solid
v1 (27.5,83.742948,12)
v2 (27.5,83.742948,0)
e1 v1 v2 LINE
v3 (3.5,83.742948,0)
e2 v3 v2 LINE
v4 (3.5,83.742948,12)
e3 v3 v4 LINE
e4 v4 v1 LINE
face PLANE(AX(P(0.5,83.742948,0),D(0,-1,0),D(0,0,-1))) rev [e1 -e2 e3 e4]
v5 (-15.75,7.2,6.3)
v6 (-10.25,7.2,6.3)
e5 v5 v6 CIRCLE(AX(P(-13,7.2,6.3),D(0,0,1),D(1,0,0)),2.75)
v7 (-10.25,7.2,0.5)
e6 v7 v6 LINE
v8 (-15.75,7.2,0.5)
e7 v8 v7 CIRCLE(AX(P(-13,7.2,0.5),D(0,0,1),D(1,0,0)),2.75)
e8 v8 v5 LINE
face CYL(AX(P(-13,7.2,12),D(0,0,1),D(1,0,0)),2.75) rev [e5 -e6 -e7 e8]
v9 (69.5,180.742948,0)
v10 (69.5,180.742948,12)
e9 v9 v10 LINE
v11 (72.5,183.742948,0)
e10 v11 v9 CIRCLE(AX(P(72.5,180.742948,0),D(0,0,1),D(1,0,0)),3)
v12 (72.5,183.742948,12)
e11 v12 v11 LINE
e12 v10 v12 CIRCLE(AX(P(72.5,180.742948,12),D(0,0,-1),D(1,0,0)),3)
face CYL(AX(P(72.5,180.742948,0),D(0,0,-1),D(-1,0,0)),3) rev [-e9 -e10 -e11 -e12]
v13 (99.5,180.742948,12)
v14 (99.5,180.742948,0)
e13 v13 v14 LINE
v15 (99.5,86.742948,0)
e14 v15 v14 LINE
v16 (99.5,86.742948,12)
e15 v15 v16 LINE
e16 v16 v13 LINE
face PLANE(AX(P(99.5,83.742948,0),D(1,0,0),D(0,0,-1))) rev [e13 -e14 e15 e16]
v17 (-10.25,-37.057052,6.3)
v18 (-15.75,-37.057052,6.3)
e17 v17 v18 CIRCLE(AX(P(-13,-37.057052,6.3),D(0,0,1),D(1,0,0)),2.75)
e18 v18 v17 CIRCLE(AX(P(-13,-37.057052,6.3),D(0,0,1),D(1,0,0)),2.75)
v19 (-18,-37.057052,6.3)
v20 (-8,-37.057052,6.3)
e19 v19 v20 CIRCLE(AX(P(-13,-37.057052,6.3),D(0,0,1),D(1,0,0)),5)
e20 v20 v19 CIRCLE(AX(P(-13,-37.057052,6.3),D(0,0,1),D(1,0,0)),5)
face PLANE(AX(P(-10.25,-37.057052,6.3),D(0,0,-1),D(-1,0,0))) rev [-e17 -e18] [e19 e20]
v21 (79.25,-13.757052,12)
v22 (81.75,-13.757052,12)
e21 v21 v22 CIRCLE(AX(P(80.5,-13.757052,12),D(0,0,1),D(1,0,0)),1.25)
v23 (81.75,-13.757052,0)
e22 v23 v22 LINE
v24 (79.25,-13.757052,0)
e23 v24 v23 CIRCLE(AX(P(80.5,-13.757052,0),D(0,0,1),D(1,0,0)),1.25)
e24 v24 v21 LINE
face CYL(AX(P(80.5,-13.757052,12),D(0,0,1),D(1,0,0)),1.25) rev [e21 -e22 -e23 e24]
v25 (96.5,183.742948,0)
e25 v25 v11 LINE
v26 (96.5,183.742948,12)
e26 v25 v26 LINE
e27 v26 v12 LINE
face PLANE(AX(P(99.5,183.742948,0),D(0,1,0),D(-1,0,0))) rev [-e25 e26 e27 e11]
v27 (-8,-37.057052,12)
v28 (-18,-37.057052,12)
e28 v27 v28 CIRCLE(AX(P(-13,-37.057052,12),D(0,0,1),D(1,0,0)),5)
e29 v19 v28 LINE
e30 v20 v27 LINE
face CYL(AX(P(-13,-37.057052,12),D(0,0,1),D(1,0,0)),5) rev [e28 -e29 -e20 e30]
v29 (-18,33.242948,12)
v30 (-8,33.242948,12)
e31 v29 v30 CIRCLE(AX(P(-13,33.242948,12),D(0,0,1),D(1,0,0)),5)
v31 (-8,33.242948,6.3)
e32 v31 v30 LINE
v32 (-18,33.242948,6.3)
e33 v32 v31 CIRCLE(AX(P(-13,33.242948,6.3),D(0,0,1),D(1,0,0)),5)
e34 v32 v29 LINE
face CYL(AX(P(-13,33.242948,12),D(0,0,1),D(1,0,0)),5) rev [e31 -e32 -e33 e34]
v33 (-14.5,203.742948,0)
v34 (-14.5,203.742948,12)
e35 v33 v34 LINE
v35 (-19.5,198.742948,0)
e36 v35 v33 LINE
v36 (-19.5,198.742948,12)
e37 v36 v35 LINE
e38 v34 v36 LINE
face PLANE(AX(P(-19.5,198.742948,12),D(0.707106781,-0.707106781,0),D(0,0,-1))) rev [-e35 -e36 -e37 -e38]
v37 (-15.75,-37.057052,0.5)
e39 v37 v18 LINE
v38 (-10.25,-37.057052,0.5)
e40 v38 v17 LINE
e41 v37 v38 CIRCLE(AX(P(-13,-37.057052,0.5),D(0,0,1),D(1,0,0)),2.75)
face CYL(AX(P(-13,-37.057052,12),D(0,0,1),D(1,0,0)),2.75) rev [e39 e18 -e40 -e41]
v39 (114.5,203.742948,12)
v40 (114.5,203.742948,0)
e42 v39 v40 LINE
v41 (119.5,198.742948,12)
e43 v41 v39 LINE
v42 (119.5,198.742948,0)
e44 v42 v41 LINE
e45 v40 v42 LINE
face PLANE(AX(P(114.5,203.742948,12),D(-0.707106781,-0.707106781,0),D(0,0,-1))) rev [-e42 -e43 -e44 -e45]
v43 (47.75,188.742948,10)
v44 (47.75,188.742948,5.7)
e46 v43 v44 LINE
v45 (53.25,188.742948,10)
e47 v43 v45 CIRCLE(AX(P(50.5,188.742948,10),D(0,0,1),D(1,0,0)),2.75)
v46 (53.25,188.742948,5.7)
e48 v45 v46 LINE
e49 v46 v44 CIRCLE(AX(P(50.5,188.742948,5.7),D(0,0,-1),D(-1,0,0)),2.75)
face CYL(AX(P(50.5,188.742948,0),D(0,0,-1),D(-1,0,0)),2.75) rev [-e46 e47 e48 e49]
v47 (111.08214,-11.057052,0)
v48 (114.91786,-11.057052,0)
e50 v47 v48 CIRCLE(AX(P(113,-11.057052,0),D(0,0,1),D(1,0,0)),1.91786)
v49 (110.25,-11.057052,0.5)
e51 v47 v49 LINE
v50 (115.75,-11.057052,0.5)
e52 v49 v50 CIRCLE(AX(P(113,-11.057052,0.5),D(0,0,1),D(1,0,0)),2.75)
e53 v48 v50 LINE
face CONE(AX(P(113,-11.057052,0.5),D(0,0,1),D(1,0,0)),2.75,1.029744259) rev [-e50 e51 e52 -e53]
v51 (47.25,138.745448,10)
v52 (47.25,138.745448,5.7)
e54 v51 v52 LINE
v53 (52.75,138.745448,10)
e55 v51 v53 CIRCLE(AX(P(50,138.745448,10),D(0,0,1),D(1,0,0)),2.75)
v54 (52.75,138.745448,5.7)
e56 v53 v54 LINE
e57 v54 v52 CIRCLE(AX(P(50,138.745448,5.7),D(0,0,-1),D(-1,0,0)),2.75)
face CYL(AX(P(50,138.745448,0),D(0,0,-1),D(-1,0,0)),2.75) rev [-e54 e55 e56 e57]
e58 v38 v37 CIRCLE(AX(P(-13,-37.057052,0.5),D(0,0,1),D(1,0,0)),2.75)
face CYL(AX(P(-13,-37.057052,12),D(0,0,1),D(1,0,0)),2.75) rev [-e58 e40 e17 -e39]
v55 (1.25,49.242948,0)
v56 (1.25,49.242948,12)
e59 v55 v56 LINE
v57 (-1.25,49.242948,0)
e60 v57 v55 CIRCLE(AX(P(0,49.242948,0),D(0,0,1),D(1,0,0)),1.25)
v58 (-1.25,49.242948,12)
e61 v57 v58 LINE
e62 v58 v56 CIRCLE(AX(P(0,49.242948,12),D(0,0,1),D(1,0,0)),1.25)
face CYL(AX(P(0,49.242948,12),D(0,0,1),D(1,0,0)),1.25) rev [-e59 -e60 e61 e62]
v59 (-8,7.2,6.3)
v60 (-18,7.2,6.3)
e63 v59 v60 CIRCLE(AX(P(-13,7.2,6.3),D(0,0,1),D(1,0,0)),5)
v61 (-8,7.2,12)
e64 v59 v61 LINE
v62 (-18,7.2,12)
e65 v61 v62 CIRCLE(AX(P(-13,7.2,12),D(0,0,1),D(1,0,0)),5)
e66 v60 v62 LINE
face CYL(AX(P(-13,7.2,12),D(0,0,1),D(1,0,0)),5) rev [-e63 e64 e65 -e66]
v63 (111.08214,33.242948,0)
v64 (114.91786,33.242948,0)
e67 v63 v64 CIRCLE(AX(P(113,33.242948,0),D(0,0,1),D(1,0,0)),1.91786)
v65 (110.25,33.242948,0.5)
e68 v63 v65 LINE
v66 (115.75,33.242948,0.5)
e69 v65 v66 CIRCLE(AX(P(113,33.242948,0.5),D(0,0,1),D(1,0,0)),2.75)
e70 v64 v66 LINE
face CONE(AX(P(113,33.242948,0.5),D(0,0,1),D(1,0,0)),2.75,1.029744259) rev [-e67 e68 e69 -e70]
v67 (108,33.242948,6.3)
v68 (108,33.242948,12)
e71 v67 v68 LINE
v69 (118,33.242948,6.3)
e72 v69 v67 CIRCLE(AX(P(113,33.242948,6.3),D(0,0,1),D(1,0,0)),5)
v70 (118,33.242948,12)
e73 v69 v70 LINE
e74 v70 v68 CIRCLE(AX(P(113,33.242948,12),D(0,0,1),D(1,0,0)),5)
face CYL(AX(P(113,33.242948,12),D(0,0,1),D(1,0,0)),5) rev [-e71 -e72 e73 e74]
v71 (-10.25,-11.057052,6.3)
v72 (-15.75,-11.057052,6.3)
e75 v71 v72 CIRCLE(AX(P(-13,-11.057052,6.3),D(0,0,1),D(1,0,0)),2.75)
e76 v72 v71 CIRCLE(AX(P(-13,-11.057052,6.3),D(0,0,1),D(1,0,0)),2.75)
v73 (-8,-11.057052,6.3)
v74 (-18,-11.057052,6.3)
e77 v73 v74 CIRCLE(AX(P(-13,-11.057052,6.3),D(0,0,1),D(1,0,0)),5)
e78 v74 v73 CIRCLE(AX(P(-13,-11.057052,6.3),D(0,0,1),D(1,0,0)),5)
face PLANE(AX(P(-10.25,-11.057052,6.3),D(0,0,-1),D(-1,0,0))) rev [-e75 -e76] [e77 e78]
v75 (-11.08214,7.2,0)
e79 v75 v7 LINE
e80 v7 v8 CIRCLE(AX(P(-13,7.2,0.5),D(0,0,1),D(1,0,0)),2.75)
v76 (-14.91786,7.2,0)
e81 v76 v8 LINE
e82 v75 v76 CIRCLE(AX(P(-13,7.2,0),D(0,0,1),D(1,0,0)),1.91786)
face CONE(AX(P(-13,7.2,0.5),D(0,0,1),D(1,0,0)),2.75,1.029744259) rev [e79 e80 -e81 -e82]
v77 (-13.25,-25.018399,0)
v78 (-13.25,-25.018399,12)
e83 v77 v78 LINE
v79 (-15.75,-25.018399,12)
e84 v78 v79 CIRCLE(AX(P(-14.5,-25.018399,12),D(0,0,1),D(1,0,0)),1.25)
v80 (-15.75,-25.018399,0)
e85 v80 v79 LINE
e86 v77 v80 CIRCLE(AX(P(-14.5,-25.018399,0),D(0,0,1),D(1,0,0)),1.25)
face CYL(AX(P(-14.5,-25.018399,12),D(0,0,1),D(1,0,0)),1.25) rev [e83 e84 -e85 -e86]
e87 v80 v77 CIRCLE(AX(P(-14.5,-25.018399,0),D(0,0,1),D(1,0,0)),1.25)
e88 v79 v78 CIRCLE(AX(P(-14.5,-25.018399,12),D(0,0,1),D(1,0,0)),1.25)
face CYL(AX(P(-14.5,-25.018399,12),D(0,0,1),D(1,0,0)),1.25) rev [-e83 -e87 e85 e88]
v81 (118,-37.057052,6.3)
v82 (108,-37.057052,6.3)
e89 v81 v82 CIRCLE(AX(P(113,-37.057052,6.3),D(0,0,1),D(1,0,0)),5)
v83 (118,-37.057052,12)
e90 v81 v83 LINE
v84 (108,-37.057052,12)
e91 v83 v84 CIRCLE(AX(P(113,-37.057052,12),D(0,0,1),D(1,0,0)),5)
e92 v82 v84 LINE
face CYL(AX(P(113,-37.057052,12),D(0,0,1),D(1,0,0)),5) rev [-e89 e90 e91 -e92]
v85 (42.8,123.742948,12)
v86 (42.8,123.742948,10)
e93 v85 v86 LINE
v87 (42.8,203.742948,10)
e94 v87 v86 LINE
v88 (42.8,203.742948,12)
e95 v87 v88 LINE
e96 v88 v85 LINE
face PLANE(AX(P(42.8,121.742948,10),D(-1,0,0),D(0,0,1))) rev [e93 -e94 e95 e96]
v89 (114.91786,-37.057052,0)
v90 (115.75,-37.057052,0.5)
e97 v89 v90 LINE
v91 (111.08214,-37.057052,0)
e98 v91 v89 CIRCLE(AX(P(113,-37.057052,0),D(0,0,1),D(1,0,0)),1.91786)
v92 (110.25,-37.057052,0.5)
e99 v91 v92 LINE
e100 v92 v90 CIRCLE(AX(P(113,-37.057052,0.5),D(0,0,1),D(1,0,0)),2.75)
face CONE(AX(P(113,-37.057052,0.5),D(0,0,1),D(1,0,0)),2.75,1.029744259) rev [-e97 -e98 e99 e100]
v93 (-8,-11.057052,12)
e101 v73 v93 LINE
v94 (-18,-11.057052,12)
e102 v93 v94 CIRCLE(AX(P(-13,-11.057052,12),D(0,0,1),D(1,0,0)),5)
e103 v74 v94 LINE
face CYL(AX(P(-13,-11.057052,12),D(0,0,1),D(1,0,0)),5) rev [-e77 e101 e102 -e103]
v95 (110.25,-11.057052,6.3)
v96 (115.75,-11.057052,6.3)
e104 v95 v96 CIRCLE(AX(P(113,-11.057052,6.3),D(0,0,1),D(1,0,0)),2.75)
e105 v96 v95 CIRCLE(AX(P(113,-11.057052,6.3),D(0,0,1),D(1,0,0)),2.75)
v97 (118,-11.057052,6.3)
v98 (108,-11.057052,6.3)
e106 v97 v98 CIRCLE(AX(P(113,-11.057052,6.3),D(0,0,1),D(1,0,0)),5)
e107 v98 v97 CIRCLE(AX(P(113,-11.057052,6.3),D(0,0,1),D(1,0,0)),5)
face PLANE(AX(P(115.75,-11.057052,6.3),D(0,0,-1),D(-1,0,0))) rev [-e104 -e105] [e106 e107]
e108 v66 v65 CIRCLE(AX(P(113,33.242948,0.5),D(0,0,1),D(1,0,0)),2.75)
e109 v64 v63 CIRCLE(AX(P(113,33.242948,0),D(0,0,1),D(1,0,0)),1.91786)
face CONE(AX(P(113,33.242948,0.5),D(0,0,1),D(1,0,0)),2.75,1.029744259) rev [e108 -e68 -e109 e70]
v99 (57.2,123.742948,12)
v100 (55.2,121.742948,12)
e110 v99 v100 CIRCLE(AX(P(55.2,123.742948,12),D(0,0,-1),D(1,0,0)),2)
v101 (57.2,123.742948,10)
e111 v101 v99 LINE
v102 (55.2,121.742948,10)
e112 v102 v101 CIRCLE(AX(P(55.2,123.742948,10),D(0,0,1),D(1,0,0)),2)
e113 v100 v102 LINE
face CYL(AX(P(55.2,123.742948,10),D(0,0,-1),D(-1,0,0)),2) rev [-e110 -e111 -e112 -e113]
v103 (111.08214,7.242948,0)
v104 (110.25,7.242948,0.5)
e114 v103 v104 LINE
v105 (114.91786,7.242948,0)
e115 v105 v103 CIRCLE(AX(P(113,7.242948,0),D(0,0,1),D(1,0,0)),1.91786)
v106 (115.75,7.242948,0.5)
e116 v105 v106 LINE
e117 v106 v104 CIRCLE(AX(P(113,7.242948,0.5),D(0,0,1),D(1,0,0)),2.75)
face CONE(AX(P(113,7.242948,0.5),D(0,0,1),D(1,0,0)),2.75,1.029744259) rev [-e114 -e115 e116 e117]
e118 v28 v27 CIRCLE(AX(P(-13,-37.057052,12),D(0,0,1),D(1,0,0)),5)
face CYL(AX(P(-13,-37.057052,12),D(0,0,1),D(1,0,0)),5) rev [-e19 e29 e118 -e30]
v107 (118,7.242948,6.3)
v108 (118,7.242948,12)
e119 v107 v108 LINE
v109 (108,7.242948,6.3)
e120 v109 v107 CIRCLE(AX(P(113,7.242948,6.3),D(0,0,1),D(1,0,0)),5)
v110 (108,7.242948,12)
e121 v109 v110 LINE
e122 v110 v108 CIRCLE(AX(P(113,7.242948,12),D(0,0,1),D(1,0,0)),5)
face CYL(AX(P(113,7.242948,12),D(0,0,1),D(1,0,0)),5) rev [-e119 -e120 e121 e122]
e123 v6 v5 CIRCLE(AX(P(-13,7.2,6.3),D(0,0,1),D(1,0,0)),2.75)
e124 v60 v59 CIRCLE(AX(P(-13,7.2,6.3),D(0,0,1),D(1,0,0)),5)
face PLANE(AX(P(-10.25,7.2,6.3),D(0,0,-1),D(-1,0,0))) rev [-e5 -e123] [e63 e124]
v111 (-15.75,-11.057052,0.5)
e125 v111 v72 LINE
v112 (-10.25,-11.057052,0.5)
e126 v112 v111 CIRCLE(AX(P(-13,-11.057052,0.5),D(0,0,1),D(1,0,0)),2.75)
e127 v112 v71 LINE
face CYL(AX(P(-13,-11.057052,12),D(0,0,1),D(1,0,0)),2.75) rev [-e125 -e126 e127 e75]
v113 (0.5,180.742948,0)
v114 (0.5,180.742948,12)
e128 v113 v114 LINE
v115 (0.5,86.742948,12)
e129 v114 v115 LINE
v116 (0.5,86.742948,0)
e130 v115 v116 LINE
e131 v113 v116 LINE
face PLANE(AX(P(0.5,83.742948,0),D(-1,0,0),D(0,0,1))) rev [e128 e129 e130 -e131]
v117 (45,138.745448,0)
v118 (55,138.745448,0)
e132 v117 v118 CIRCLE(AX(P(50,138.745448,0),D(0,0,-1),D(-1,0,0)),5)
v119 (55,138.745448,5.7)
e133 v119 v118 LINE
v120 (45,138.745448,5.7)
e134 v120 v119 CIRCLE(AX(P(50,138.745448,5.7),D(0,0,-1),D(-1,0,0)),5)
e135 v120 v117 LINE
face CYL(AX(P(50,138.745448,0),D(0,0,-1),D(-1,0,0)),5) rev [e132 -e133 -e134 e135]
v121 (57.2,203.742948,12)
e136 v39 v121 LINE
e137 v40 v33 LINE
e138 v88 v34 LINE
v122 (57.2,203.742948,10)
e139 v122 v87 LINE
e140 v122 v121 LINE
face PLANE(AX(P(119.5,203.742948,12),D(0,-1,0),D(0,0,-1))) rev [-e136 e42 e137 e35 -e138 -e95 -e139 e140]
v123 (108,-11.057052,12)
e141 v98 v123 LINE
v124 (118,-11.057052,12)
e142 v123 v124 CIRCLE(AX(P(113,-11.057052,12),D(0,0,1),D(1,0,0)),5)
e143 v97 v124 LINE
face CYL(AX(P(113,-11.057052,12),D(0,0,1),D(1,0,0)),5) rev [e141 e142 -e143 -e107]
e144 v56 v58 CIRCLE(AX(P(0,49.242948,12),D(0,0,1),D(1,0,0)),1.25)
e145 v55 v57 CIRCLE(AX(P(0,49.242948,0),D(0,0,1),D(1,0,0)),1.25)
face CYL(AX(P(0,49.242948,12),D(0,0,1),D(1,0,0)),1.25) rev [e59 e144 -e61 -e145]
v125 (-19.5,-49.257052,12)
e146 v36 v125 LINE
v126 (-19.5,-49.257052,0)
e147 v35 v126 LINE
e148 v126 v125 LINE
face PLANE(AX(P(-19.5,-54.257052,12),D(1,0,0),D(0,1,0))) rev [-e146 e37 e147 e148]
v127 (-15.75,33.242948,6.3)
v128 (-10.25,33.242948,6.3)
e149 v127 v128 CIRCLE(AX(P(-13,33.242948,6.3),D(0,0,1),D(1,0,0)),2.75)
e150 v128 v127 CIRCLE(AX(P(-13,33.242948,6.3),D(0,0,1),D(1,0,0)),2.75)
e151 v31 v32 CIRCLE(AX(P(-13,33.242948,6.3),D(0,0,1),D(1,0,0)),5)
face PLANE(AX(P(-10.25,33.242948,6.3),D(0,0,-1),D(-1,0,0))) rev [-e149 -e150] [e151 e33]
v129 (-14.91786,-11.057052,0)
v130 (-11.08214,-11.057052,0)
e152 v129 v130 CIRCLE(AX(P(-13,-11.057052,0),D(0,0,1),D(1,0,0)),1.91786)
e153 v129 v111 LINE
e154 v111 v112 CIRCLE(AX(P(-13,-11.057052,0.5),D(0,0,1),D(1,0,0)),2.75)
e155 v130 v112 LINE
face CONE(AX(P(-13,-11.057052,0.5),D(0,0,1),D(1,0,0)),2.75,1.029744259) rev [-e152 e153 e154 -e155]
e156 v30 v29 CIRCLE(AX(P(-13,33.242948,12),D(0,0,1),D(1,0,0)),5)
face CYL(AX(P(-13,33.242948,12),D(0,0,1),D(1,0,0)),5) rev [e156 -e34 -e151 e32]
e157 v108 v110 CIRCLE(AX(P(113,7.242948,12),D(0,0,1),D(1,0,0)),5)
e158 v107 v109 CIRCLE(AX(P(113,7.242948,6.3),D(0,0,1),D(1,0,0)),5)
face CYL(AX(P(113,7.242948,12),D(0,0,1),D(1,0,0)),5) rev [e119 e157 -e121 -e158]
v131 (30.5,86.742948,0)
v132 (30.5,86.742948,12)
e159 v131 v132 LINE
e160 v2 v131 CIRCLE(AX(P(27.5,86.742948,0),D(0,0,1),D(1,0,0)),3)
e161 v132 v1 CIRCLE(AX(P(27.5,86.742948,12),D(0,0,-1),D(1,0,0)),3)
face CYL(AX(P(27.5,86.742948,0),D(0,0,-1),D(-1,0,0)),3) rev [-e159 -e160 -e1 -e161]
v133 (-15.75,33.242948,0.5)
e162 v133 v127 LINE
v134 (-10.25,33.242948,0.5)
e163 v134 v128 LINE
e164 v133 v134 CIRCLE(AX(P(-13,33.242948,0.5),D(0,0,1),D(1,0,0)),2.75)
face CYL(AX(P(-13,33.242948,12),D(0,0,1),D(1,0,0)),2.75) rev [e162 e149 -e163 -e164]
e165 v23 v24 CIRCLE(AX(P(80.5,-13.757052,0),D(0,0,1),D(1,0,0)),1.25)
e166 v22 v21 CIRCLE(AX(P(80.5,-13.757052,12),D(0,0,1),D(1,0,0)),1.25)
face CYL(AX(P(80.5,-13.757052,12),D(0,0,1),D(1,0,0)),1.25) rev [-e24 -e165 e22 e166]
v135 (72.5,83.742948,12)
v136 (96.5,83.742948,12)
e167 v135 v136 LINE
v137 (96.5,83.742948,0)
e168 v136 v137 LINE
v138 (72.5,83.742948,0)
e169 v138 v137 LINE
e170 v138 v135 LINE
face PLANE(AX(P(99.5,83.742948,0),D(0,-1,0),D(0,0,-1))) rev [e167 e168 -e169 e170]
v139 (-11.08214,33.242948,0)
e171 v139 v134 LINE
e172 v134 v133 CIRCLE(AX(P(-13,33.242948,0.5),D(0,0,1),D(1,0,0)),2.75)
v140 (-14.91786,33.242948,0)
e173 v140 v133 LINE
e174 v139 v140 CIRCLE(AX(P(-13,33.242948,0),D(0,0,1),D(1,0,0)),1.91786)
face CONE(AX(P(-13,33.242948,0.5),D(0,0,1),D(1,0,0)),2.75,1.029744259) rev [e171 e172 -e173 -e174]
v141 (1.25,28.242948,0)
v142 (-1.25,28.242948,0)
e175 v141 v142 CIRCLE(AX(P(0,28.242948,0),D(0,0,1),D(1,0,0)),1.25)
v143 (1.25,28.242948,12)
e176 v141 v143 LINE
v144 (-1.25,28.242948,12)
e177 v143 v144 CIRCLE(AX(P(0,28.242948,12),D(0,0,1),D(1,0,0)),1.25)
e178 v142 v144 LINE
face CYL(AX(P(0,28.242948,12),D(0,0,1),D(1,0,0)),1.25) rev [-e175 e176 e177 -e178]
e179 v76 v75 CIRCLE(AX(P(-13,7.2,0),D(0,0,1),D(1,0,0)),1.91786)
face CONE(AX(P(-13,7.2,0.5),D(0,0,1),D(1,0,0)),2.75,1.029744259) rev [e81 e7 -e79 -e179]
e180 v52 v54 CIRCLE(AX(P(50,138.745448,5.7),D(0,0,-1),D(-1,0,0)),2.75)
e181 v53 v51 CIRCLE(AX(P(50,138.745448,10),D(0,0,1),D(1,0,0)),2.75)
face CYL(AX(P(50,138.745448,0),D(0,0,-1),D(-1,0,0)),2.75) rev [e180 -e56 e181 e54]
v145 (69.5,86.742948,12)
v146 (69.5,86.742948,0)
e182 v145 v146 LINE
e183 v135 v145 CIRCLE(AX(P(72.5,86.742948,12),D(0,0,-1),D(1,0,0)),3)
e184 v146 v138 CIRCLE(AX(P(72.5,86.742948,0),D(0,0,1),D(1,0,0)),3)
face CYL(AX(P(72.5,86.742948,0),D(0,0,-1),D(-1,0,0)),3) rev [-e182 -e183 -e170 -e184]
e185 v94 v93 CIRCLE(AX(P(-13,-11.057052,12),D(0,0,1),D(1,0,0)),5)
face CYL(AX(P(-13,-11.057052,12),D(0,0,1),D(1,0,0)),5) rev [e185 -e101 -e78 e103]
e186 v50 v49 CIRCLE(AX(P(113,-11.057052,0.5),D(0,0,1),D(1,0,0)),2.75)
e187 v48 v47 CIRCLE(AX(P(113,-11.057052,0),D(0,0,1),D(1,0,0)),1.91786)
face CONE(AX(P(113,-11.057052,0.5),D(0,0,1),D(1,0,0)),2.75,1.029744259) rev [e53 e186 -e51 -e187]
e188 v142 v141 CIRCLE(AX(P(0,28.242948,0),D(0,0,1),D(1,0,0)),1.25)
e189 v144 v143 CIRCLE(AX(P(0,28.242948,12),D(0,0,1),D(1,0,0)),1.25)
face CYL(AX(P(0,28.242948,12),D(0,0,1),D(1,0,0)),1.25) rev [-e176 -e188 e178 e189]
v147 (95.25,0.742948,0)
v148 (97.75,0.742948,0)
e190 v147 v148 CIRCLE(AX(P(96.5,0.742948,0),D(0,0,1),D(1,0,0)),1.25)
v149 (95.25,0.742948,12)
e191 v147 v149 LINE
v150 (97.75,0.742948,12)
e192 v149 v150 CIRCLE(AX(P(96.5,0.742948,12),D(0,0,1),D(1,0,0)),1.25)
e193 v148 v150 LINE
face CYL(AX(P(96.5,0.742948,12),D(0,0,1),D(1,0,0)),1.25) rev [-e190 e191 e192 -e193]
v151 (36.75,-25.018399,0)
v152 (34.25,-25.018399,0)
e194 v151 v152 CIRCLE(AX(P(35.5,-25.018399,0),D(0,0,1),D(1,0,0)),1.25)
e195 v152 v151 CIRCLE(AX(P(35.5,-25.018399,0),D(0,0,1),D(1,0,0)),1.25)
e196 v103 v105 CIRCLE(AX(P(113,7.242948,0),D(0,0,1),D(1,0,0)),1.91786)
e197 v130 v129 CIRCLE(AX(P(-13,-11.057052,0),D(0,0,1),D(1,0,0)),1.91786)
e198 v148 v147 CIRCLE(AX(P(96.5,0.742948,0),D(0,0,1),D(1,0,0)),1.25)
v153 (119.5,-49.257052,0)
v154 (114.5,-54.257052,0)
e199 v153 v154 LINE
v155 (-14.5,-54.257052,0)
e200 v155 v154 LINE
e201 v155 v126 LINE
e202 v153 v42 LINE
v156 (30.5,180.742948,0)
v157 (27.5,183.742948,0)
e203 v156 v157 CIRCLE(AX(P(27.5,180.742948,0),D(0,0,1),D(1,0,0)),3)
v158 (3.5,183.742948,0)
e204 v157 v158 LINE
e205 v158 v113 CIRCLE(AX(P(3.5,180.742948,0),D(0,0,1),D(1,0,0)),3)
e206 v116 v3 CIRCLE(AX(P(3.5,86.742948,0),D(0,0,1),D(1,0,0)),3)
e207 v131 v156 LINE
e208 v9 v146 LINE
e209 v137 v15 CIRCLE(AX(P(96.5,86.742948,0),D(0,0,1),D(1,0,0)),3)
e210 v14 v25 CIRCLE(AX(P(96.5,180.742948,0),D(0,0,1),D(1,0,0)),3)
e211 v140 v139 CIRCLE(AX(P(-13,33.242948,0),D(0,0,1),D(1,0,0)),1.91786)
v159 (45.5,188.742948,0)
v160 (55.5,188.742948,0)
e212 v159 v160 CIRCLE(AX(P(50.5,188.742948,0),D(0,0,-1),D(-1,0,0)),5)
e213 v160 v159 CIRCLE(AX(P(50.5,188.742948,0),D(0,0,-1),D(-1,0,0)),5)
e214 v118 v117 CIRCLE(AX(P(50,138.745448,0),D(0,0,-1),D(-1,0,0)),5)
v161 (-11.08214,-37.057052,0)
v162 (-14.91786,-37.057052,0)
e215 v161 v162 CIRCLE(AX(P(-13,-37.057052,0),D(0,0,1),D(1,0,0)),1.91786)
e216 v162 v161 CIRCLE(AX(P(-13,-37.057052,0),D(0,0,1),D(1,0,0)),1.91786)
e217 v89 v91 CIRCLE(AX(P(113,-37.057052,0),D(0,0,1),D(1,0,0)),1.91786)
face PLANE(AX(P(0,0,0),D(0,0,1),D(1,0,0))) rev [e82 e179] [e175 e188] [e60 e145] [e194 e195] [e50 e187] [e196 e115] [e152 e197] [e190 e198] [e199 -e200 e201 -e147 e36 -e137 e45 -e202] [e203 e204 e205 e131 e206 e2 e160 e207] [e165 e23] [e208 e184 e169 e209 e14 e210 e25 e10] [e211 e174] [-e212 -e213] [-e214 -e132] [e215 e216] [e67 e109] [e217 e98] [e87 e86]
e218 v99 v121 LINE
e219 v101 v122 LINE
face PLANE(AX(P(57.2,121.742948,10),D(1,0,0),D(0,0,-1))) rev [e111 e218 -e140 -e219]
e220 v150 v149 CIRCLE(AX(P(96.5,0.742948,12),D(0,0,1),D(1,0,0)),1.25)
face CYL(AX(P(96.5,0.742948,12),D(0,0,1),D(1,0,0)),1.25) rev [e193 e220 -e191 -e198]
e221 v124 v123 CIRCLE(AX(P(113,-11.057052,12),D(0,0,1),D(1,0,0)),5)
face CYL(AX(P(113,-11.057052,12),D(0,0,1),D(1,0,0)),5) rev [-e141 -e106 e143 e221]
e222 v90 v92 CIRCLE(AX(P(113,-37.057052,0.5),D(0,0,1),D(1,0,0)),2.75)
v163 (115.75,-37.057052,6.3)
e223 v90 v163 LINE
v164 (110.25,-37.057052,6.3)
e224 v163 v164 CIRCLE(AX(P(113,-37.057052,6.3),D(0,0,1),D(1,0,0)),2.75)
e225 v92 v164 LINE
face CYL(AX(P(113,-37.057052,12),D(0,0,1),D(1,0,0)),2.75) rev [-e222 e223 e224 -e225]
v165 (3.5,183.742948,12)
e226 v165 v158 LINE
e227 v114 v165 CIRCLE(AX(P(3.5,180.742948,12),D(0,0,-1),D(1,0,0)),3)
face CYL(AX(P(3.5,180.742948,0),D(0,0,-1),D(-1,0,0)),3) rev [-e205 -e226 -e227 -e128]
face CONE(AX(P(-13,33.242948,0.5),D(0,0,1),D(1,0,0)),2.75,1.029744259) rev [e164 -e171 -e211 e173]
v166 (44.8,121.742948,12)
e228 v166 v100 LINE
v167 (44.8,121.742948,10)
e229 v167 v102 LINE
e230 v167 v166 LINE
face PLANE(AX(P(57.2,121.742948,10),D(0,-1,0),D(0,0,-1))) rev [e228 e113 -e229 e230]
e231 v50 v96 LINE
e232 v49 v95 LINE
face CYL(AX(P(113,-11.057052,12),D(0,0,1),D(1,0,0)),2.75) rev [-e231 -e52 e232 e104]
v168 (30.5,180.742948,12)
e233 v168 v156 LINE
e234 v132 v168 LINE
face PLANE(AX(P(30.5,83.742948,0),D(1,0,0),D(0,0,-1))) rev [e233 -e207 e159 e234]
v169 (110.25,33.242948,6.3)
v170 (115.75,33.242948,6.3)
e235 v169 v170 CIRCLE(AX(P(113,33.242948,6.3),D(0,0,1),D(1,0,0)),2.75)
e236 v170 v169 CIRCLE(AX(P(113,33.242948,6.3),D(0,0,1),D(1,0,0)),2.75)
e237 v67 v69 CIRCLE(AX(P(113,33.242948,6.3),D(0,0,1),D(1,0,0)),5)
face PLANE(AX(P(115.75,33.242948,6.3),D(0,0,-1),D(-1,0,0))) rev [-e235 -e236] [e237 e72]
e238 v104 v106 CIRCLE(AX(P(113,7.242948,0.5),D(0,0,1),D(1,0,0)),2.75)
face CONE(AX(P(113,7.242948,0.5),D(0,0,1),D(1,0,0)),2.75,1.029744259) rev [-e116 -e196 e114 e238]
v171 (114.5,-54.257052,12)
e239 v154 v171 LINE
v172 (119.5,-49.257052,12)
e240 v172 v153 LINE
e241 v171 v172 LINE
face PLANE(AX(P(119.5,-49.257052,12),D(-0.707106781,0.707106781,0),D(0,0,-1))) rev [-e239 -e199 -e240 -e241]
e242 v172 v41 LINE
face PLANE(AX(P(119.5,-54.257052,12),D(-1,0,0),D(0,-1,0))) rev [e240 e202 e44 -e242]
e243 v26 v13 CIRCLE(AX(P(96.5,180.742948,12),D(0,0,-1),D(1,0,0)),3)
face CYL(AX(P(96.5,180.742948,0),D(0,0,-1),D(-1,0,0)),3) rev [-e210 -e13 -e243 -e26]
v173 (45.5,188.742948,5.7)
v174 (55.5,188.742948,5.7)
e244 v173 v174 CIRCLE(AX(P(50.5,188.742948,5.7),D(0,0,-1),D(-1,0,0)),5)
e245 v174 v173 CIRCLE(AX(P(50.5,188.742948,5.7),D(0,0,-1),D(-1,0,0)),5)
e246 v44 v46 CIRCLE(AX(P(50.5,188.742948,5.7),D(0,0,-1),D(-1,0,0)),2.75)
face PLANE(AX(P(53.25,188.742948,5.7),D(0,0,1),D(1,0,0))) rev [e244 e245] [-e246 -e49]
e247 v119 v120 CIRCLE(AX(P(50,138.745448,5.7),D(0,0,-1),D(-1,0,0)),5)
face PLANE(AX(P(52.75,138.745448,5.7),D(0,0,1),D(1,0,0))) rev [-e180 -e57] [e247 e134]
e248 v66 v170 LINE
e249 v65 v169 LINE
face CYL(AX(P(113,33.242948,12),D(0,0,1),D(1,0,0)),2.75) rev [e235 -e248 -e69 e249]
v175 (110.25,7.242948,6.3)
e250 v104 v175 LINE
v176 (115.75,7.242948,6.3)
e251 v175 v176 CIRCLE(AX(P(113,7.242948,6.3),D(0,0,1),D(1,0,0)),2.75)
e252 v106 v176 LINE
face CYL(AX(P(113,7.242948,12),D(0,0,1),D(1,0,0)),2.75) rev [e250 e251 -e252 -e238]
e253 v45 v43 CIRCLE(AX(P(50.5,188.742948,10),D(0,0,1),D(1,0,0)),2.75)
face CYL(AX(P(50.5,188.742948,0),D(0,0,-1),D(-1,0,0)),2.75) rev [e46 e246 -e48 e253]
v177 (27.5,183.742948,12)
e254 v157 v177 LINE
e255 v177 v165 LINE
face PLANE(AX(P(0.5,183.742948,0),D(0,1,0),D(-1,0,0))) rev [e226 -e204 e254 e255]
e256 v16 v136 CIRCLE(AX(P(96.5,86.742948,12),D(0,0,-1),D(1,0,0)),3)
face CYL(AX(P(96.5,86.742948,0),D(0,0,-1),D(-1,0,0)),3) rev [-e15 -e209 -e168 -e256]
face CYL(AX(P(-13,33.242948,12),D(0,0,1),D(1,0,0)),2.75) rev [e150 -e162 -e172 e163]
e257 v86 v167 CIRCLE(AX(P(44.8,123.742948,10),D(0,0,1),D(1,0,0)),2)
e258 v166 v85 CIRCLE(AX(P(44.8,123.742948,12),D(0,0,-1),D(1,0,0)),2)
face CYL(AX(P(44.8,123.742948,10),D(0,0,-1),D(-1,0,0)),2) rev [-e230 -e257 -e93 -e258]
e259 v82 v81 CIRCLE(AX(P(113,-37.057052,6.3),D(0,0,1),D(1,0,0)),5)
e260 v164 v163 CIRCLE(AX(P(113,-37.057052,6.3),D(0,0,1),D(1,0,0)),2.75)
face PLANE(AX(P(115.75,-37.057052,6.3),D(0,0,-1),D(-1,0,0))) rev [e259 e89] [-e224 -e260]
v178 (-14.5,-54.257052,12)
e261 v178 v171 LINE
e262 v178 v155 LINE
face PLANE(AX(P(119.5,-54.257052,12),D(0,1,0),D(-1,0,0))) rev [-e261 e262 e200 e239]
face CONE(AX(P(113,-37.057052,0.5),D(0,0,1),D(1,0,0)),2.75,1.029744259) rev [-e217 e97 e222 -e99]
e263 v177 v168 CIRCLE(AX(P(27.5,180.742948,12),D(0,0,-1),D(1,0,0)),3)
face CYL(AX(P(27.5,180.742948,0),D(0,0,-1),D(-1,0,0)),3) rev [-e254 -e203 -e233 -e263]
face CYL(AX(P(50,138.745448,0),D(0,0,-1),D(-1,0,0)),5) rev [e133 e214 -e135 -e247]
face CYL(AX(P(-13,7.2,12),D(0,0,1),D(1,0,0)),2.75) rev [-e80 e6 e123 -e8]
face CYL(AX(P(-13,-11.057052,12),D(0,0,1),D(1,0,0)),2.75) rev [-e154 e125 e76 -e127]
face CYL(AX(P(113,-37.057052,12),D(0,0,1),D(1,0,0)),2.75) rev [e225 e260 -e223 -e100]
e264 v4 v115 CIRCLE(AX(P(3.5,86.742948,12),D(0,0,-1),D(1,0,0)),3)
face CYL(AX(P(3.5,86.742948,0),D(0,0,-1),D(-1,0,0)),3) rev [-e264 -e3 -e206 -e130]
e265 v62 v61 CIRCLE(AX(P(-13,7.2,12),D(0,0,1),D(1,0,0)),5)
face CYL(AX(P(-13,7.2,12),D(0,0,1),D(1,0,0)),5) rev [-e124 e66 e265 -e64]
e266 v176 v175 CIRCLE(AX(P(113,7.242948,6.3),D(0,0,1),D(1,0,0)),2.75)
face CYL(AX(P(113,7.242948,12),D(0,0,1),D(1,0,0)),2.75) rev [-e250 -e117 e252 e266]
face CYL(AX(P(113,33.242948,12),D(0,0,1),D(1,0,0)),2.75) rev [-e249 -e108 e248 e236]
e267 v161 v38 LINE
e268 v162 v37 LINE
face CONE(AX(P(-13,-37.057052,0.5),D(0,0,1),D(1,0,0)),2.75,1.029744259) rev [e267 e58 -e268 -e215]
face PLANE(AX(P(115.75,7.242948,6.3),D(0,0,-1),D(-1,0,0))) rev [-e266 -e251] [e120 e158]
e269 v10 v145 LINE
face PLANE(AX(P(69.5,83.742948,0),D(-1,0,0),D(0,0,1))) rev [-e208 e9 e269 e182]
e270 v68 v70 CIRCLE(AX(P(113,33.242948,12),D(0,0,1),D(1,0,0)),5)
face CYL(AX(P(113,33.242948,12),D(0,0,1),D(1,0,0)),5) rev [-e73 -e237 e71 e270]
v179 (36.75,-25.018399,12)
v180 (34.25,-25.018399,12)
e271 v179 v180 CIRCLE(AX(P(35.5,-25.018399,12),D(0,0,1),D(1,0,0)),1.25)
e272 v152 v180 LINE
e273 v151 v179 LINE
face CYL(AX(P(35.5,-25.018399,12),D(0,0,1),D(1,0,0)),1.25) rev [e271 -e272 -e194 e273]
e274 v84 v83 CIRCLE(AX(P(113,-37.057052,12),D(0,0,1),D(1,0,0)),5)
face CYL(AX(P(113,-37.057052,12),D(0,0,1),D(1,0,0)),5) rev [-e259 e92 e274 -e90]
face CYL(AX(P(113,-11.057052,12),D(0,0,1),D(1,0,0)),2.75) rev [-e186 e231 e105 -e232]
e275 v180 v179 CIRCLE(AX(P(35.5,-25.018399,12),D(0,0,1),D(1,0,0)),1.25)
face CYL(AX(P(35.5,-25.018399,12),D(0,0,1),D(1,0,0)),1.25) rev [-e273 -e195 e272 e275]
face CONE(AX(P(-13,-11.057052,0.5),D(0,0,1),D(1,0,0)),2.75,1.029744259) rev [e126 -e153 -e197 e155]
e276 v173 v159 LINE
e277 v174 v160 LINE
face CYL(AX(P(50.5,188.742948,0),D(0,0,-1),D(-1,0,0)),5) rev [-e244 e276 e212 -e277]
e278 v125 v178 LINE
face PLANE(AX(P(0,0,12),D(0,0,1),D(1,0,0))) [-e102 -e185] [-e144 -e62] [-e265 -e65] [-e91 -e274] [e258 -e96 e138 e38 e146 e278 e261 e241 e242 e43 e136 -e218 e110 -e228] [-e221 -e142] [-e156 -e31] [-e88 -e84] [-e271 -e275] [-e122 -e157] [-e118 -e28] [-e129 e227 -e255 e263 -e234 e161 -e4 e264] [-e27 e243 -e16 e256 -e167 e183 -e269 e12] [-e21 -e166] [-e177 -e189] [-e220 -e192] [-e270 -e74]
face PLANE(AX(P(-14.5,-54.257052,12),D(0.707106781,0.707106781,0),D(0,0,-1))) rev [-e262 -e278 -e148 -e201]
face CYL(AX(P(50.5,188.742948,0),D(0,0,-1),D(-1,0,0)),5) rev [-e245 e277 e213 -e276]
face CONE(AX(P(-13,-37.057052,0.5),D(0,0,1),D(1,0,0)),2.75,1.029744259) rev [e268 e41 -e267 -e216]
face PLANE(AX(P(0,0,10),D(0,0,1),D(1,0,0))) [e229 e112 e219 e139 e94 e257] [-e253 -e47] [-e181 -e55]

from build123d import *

# Parameters (mm, degrees)
SKETCH1_W                                            = 139
SKETCH1_H                                            = 258
BOSS_EXTRUDE1_DEPTH                                  = 12
CHAMFER1_SIZE                                        = 5
SKETCH2_W                                            = 30
SKETCH2_H                                            = 100
CUT_EXTRUDE1_DEPTH                                   = 237.506741929
SKETCH3_W                                            = 14.4
SKETCH3_H                                            = 82
CUT_EXTRUDE2_DEPTH                                   = 2
FILLET1_R                                            = 2
M3_TAPPED_HOLE1_D                                    = 2.5
M3_TAPPED_HOLE2_D                                    = 2.5
CBORE_FOR_M5_HEXAGON_SOCKET_HEAD_CAP_SCR_D           = 5.5
CBORE_FOR_M5_HEXAGON_SOCKET_HEAD_CAP_SCR_CBORE_D     = 10
CBORE_FOR_M5_HEXAGON_SOCKET_HEAD_CAP_SCR_CBORE_DEPTH = 5.7
FILLET2_R                                            = 3
CBORE_FOR_M5_HEXAGON_SOCKET_HEAD_CAP_2_D             = 5.5
CBORE_FOR_M5_HEXAGON_SOCKET_HEAD_CAP_2_DEPTH         = 11.5
CBORE_FOR_M5_HEXAGON_SOCKET_HEAD_CAP_2_CBORE_D       = 10
CBORE_FOR_M5_HEXAGON_SOCKET_HEAD_CAP_2_CBORE_DEPTH   = 5.7
CBORE_FOR_M5_HEXAGON_SOCKET_HEAD_CAP_2_TIP           = 1.652366702


with BuildPart() as part:
    # Sketch1 → Boss-Extrude1 (new body)
    with BuildSketch(Plane.XY):
        with Locations((50, 74.74294829)):
            Rectangle(SKETCH1_W, SKETCH1_H)
    extrude(amount=BOSS_EXTRUDE1_DEPTH)

    # Chamfer1
    chamfer1_edges = [part.edges().sort_by_distance(p)[0] for p in [
        (119.5, -54.25705171, 6),
        (-19.5, -54.25705171, 6),
        (-19.5, 203.74294829, 6),
        (119.5, 203.74294829, 6),
    ]]
    chamfer(chamfer1_edges, length=CHAMFER1_SIZE)

    # Sketch2 → Cut-Extrude1 (cut, through all)
    with BuildSketch(Plane.XY.offset(12)):
        with Locations((84.5, 133.74294829)):
            Rectangle(SKETCH2_W, SKETCH2_H)
        with Locations((15.5, 133.74294829)):
            Rectangle(SKETCH2_W, SKETCH2_H)
    extrude(amount=-CUT_EXTRUDE1_DEPTH, mode=Mode.SUBTRACT)

    # Sketch3 → Cut-Extrude2 (cut)
    with BuildSketch(Plane.XY.offset(12)):
        with Locations((50, 162.74294829)):
            Rectangle(SKETCH3_W, SKETCH3_H)
    extrude(amount=-CUT_EXTRUDE2_DEPTH, mode=Mode.SUBTRACT)

    # Fillet1
    fillet1_edges = [part.edges().sort_by_distance(p)[0] for p in [
        (57.2, 121.74294829, 11),
        (42.8, 121.74294829, 11),
    ]]
    fillet(fillet1_edges, radius=FILLET1_R)

    # M3 Tapped Hole1 (through all)
    with Locations(Plane.XY.offset(12)):
        with Locations((-14.5, -25.018399206), (35.5, -25.018399206), (96.5, 0.74294829), (80.5, -13.75705171)):
            Hole(M3_TAPPED_HOLE1_D / 2)

    # M3 Tapped Hole2 (through all)
    with Locations(Plane.XY.offset(12)):
        with Locations((0, 49.24294829), (0, 28.24294829)):
            Hole(M3_TAPPED_HOLE2_D / 2)

    # CBORE for M5 Hexagon socket head cap scr (through all)
    with Locations(Plane(origin=(0, 0, 0), x_dir=(-1, 0, 0), z_dir=(0, 0, -1))):
        with Locations((-50.5, 188.74294829), (-50, 138.745448352)):
            CounterBoreHole(CBORE_FOR_M5_HEXAGON_SOCKET_HEAD_CAP_SCR_D / 2, CBORE_FOR_M5_HEXAGON_SOCKET_HEAD_CAP_SCR_CBORE_D / 2, CBORE_FOR_M5_HEXAGON_SOCKET_HEAD_CAP_SCR_CBORE_DEPTH)

    # Fillet2
    fillet2_edges = [part.edges().sort_by_distance(p)[0] for p in [
        (99.5, 183.74294829, 6),
        (99.5, 83.74294829, 6),
        (69.5, 83.74294829, 6),
        (69.5, 183.74294829, 6),
        (30.5, 83.74294829, 6),
        (0.5, 83.74294829, 6),
        (0.5, 183.74294829, 6),
        (30.5, 183.74294829, 6),
    ]]
    fillet(fillet2_edges, radius=FILLET2_R)

    # CBORE for M5 Hexagon socket head cap 2
    with Locations(Plane.XY.offset(12)):
        with Locations((113, -37.05705171), (113, -11.05705171), (113, 7.24294829), (113, 33.24294829), (-13, -11.05705171), (-13, 7.2), (-13, -37.05705171), (-13, 33.24294829)):
            CounterBoreHole(CBORE_FOR_M5_HEXAGON_SOCKET_HEAD_CAP_2_D / 2, CBORE_FOR_M5_HEXAGON_SOCKET_HEAD_CAP_2_CBORE_D / 2, CBORE_FOR_M5_HEXAGON_SOCKET_HEAD_CAP_2_CBORE_DEPTH, depth=CBORE_FOR_M5_HEXAGON_SOCKET_HEAD_CAP_2_DEPTH)
            with Locations((0, 0, -(CBORE_FOR_M5_HEXAGON_SOCKET_HEAD_CAP_2_DEPTH + CBORE_FOR_M5_HEXAGON_SOCKET_HEAD_CAP_2_TIP / 2))):  # 118° drill point
                Cone(0, CBORE_FOR_M5_HEXAGON_SOCKET_HEAD_CAP_2_D / 2, CBORE_FOR_M5_HEXAGON_SOCKET_HEAD_CAP_2_TIP, mode=Mode.SUBTRACT)


solid = part.part
